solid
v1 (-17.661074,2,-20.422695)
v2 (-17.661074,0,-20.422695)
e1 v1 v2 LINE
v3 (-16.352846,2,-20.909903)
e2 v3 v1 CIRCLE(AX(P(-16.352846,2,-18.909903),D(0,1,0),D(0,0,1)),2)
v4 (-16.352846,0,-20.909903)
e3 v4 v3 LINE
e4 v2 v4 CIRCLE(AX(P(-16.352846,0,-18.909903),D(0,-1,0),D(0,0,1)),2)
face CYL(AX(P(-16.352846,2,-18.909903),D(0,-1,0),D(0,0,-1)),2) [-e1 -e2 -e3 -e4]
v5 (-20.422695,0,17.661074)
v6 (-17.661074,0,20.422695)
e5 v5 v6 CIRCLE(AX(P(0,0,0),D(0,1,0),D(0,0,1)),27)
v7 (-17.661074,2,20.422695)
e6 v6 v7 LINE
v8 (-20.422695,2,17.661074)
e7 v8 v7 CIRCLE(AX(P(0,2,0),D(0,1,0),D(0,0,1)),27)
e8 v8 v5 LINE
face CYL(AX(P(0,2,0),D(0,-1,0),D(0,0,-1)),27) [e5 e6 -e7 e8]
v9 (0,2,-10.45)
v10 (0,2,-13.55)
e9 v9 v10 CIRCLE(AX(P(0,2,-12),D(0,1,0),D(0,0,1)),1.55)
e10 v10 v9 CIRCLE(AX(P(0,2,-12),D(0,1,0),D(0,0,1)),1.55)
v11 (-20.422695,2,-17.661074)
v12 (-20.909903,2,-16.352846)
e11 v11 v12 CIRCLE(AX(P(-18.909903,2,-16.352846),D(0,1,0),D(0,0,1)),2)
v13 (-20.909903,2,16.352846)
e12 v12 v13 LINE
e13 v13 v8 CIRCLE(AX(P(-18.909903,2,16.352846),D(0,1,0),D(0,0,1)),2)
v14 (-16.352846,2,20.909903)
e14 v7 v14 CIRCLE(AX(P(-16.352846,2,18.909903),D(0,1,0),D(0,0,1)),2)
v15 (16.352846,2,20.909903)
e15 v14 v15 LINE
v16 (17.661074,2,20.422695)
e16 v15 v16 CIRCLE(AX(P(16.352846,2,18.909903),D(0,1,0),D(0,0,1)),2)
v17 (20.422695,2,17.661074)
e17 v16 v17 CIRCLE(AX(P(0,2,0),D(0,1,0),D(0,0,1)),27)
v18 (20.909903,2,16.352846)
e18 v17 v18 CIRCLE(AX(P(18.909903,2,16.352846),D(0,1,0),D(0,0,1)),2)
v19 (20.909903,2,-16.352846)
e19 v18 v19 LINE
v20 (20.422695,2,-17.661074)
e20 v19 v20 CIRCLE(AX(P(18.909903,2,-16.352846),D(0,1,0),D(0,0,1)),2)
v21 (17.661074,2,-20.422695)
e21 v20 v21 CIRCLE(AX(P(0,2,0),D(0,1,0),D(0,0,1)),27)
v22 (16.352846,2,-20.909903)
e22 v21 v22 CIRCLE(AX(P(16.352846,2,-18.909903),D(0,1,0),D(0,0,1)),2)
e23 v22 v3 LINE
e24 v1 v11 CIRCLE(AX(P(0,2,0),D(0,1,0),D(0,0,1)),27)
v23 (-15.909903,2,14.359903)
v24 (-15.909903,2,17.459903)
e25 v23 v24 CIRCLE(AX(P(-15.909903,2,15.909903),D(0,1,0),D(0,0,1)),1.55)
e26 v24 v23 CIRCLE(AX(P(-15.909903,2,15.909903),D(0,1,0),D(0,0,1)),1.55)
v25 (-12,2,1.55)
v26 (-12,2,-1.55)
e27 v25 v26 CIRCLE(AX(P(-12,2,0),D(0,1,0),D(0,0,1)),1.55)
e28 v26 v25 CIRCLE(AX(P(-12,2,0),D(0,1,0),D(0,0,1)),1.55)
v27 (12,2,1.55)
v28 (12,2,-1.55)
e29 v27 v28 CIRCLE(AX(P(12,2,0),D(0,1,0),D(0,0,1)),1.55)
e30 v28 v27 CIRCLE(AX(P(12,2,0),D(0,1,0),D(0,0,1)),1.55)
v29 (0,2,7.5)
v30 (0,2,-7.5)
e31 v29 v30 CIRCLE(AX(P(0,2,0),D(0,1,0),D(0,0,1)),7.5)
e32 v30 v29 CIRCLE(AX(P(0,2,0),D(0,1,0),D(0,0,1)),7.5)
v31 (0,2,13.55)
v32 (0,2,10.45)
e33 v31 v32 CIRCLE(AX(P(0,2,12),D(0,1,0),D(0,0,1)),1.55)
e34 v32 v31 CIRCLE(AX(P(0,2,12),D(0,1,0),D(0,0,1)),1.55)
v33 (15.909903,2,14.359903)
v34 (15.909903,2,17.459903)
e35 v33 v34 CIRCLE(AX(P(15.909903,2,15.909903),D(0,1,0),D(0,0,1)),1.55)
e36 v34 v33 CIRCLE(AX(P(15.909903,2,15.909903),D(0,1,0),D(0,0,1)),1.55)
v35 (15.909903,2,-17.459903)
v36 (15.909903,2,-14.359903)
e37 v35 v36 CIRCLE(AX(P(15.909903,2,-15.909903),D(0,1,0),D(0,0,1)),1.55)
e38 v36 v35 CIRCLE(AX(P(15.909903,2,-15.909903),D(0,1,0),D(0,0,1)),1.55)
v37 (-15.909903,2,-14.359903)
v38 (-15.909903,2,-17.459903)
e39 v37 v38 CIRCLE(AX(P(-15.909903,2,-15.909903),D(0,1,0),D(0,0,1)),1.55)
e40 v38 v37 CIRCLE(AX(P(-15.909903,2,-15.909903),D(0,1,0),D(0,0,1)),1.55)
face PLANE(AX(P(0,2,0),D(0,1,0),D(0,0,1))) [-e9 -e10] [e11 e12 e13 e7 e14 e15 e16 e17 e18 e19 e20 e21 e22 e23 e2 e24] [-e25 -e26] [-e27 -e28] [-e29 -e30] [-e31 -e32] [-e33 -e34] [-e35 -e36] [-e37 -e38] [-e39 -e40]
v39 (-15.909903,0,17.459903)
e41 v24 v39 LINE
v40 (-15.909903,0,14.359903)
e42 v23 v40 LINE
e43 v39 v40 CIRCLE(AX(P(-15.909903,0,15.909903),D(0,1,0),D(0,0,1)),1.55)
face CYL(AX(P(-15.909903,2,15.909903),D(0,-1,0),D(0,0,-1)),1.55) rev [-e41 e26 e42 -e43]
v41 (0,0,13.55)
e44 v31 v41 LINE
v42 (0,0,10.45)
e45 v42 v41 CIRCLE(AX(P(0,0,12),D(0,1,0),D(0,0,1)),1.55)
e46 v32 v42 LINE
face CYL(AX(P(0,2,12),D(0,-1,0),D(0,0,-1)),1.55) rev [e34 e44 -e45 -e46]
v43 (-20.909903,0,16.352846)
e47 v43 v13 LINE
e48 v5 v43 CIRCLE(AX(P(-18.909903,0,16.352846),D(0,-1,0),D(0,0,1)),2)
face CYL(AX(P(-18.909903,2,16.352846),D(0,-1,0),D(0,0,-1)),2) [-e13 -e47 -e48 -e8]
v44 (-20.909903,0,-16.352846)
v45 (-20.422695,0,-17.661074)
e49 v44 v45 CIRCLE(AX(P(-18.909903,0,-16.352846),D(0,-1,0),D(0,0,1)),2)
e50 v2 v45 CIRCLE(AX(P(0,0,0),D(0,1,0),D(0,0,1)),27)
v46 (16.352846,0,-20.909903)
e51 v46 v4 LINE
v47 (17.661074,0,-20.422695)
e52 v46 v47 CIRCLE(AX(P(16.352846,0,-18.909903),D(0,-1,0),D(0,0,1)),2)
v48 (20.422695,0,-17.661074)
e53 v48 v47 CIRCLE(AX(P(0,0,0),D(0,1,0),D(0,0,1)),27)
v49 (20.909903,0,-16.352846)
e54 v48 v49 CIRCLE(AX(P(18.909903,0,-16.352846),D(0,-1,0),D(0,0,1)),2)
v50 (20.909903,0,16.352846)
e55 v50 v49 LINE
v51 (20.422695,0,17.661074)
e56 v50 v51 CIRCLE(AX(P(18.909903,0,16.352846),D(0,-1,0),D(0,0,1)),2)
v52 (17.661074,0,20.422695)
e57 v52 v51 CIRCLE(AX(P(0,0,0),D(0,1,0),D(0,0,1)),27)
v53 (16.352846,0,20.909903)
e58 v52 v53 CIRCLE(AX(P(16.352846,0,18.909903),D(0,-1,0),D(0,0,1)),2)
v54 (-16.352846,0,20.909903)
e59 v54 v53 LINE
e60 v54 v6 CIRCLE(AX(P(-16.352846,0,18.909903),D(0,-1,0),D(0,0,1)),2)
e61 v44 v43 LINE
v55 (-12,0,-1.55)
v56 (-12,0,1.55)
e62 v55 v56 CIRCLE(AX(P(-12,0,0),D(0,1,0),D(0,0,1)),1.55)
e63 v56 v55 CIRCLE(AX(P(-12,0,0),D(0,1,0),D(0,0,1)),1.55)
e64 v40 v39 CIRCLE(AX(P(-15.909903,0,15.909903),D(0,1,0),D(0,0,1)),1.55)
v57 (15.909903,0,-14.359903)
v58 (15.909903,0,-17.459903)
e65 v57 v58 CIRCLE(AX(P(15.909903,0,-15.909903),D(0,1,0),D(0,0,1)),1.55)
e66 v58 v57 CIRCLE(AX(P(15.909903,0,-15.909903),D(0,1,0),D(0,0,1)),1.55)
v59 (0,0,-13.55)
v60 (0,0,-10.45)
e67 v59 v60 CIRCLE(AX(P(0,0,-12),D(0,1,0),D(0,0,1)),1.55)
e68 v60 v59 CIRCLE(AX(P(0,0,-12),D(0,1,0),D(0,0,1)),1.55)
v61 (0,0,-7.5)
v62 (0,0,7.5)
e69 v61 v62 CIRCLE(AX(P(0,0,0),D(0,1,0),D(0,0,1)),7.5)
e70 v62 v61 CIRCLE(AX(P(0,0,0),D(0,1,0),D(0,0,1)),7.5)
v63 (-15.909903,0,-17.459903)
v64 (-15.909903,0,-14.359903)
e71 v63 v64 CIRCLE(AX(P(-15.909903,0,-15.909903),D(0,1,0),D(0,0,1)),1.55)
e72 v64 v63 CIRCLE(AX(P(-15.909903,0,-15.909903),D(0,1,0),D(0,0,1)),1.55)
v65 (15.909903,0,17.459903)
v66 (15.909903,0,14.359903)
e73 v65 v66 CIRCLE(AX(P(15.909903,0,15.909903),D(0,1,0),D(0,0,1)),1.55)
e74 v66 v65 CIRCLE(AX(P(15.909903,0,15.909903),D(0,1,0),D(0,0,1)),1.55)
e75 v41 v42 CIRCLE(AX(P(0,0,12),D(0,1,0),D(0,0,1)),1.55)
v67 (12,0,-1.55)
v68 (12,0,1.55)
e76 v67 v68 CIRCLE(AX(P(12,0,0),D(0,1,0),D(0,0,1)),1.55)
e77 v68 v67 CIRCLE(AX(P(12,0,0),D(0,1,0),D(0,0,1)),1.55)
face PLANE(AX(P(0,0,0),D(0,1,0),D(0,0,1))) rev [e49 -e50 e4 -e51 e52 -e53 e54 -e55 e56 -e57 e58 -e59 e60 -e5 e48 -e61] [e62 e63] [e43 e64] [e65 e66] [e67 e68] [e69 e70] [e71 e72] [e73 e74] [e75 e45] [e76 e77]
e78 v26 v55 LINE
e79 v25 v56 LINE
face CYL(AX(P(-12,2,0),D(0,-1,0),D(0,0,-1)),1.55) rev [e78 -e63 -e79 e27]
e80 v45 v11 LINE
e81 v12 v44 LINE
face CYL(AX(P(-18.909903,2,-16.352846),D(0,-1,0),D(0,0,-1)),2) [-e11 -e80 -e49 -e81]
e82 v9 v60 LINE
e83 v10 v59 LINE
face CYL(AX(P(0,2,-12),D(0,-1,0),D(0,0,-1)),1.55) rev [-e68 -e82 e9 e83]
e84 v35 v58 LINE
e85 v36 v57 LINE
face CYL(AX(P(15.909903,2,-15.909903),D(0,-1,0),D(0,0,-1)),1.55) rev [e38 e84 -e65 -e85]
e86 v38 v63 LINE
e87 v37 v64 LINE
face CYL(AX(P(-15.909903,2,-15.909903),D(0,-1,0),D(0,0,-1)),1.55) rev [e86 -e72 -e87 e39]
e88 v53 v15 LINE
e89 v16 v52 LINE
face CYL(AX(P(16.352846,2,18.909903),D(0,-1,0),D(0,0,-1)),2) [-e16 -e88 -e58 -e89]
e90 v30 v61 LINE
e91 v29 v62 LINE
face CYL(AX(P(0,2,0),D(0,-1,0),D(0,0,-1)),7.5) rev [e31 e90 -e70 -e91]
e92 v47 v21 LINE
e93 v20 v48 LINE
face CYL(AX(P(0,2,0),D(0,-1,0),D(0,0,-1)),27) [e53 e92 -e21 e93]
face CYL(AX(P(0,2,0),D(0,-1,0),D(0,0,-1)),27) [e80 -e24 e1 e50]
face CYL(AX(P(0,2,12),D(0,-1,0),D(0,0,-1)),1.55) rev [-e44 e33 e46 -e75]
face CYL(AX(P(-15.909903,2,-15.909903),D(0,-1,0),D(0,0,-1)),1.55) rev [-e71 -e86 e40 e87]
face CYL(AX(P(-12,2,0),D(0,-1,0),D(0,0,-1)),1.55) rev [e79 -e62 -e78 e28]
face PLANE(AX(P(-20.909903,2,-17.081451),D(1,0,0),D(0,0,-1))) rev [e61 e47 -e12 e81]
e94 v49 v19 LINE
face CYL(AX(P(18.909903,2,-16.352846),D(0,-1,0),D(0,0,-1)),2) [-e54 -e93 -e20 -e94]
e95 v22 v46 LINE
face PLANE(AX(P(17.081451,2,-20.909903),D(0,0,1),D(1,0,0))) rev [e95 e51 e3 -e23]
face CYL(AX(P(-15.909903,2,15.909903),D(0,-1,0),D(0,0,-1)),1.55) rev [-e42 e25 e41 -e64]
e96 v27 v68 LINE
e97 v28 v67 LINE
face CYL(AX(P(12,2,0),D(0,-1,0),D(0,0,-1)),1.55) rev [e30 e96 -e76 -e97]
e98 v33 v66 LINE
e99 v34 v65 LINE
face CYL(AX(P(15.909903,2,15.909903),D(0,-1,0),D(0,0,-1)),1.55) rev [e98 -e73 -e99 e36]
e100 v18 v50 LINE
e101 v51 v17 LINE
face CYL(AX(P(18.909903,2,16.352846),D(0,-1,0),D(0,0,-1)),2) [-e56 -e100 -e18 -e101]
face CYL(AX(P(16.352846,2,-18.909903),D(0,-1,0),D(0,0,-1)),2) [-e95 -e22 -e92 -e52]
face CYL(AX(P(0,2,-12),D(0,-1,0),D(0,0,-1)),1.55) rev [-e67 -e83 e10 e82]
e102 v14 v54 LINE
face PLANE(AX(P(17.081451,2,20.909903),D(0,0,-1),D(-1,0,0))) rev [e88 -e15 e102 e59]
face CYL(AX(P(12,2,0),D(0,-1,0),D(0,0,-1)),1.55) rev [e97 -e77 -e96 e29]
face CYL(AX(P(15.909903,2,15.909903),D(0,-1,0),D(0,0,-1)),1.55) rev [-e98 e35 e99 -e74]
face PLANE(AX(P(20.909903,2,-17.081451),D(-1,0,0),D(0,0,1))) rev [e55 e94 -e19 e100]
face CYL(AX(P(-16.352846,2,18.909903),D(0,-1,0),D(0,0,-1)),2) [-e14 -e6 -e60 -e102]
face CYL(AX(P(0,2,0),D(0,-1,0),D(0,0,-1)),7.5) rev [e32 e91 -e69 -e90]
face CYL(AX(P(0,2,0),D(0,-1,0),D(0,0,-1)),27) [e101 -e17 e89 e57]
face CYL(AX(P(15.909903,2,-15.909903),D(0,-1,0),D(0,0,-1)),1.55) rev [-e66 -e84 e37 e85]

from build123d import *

# Parameters (mm, degrees)
SKETCH_1_R      = 7.5
SKETCH_1_R_2    = 1.55
EXTRUDE_1_DEPTH = 2
FILLET_1_R      = 2


with BuildPart() as part:
    # 草图1 → 凸台-拉伸1 (new body)
    with BuildSketch(Plane(origin=(0, 0, 0), x_dir=(1, 0, 0), z_dir=(0, 1, 0))):
        with BuildLine():
            Line((17.081451175, -20.909902577), (-17.081451175, -20.909902577))
            ThreePointArc((-17.081451175, -20.909902577), (-19.091883092, -19.091883092), (-20.909902577, -17.081451175))
            Line((-20.909902577, -17.081451175), (-20.909902577, 17.081451175))
            ThreePointArc((-20.909902577, 17.081451175), (-19.091883092, 19.091883092), (-17.081451175, 20.909902577))
            Line((-17.081451175, 20.909902577), (17.081451175, 20.909902577))
            ThreePointArc((17.081451175, 20.909902577), (19.091883092, 19.091883092), (20.909902577, 17.081451175))
            Line((20.909902577, 17.081451175), (20.909902577, -17.081451175))
            ThreePointArc((20.909902577, -17.081451175), (19.091883092, -19.091883092), (17.081451175, -20.909902577))
        make_face()
        with Locations(Location((0, 0, 0), (0, 0, 270))):
            Circle(SKETCH_1_R, mode=Mode.SUBTRACT)
        with Locations(Location((12, 0, 0), (0, 0, 270))):
            Circle(SKETCH_1_R_2, mode=Mode.SUBTRACT)
        with Locations(Location((15.909902577, 15.909902577, 0), (0, 0, 270))):
            Circle(SKETCH_1_R_2, mode=Mode.SUBTRACT)
        with Locations(Location((0, -12, 0), (0, 0, 270))):
            Circle(SKETCH_1_R_2, mode=Mode.SUBTRACT)
        with Locations(Location((15.909902577, -15.909902577, 0), (0, 0, 270))):
            Circle(SKETCH_1_R_2, mode=Mode.SUBTRACT)
        with Locations(Location((-12, 0, 0), (0, 0, 270))):
            Circle(SKETCH_1_R_2, mode=Mode.SUBTRACT)
        with Locations(Location((-15.909902577, -15.909902577, 0), (0, 0, 270))):
            Circle(SKETCH_1_R_2, mode=Mode.SUBTRACT)
        with Locations(Location((0, 12, 0), (0, 0, 270))):
            Circle(SKETCH_1_R_2, mode=Mode.SUBTRACT)
        with Locations(Location((-15.909902577, 15.909902577, 0), (0, 0, 270))):
            Circle(SKETCH_1_R_2, mode=Mode.SUBTRACT)
    extrude(amount=EXTRUDE_1_DEPTH)

    # 圆角1
    fillet_1_edges = [part.edges().sort_by_distance(p)[0] for p in [
        (17.081451175, 1, 20.909902577),
        (-17.081451175, 1, 20.909902577),
        (-20.909902577, 1, 17.081451175),
        (-20.909902577, 1, -17.081451175),
        (-17.081451175, 1, -20.909902577),
        (17.081451175, 1, -20.909902577),
        (20.909902577, 1, -17.081451175),
        (20.909902577, 1, 17.081451175),
    ]]
    fillet(fillet_1_edges, radius=FILLET_1_R)


solid = part.part
